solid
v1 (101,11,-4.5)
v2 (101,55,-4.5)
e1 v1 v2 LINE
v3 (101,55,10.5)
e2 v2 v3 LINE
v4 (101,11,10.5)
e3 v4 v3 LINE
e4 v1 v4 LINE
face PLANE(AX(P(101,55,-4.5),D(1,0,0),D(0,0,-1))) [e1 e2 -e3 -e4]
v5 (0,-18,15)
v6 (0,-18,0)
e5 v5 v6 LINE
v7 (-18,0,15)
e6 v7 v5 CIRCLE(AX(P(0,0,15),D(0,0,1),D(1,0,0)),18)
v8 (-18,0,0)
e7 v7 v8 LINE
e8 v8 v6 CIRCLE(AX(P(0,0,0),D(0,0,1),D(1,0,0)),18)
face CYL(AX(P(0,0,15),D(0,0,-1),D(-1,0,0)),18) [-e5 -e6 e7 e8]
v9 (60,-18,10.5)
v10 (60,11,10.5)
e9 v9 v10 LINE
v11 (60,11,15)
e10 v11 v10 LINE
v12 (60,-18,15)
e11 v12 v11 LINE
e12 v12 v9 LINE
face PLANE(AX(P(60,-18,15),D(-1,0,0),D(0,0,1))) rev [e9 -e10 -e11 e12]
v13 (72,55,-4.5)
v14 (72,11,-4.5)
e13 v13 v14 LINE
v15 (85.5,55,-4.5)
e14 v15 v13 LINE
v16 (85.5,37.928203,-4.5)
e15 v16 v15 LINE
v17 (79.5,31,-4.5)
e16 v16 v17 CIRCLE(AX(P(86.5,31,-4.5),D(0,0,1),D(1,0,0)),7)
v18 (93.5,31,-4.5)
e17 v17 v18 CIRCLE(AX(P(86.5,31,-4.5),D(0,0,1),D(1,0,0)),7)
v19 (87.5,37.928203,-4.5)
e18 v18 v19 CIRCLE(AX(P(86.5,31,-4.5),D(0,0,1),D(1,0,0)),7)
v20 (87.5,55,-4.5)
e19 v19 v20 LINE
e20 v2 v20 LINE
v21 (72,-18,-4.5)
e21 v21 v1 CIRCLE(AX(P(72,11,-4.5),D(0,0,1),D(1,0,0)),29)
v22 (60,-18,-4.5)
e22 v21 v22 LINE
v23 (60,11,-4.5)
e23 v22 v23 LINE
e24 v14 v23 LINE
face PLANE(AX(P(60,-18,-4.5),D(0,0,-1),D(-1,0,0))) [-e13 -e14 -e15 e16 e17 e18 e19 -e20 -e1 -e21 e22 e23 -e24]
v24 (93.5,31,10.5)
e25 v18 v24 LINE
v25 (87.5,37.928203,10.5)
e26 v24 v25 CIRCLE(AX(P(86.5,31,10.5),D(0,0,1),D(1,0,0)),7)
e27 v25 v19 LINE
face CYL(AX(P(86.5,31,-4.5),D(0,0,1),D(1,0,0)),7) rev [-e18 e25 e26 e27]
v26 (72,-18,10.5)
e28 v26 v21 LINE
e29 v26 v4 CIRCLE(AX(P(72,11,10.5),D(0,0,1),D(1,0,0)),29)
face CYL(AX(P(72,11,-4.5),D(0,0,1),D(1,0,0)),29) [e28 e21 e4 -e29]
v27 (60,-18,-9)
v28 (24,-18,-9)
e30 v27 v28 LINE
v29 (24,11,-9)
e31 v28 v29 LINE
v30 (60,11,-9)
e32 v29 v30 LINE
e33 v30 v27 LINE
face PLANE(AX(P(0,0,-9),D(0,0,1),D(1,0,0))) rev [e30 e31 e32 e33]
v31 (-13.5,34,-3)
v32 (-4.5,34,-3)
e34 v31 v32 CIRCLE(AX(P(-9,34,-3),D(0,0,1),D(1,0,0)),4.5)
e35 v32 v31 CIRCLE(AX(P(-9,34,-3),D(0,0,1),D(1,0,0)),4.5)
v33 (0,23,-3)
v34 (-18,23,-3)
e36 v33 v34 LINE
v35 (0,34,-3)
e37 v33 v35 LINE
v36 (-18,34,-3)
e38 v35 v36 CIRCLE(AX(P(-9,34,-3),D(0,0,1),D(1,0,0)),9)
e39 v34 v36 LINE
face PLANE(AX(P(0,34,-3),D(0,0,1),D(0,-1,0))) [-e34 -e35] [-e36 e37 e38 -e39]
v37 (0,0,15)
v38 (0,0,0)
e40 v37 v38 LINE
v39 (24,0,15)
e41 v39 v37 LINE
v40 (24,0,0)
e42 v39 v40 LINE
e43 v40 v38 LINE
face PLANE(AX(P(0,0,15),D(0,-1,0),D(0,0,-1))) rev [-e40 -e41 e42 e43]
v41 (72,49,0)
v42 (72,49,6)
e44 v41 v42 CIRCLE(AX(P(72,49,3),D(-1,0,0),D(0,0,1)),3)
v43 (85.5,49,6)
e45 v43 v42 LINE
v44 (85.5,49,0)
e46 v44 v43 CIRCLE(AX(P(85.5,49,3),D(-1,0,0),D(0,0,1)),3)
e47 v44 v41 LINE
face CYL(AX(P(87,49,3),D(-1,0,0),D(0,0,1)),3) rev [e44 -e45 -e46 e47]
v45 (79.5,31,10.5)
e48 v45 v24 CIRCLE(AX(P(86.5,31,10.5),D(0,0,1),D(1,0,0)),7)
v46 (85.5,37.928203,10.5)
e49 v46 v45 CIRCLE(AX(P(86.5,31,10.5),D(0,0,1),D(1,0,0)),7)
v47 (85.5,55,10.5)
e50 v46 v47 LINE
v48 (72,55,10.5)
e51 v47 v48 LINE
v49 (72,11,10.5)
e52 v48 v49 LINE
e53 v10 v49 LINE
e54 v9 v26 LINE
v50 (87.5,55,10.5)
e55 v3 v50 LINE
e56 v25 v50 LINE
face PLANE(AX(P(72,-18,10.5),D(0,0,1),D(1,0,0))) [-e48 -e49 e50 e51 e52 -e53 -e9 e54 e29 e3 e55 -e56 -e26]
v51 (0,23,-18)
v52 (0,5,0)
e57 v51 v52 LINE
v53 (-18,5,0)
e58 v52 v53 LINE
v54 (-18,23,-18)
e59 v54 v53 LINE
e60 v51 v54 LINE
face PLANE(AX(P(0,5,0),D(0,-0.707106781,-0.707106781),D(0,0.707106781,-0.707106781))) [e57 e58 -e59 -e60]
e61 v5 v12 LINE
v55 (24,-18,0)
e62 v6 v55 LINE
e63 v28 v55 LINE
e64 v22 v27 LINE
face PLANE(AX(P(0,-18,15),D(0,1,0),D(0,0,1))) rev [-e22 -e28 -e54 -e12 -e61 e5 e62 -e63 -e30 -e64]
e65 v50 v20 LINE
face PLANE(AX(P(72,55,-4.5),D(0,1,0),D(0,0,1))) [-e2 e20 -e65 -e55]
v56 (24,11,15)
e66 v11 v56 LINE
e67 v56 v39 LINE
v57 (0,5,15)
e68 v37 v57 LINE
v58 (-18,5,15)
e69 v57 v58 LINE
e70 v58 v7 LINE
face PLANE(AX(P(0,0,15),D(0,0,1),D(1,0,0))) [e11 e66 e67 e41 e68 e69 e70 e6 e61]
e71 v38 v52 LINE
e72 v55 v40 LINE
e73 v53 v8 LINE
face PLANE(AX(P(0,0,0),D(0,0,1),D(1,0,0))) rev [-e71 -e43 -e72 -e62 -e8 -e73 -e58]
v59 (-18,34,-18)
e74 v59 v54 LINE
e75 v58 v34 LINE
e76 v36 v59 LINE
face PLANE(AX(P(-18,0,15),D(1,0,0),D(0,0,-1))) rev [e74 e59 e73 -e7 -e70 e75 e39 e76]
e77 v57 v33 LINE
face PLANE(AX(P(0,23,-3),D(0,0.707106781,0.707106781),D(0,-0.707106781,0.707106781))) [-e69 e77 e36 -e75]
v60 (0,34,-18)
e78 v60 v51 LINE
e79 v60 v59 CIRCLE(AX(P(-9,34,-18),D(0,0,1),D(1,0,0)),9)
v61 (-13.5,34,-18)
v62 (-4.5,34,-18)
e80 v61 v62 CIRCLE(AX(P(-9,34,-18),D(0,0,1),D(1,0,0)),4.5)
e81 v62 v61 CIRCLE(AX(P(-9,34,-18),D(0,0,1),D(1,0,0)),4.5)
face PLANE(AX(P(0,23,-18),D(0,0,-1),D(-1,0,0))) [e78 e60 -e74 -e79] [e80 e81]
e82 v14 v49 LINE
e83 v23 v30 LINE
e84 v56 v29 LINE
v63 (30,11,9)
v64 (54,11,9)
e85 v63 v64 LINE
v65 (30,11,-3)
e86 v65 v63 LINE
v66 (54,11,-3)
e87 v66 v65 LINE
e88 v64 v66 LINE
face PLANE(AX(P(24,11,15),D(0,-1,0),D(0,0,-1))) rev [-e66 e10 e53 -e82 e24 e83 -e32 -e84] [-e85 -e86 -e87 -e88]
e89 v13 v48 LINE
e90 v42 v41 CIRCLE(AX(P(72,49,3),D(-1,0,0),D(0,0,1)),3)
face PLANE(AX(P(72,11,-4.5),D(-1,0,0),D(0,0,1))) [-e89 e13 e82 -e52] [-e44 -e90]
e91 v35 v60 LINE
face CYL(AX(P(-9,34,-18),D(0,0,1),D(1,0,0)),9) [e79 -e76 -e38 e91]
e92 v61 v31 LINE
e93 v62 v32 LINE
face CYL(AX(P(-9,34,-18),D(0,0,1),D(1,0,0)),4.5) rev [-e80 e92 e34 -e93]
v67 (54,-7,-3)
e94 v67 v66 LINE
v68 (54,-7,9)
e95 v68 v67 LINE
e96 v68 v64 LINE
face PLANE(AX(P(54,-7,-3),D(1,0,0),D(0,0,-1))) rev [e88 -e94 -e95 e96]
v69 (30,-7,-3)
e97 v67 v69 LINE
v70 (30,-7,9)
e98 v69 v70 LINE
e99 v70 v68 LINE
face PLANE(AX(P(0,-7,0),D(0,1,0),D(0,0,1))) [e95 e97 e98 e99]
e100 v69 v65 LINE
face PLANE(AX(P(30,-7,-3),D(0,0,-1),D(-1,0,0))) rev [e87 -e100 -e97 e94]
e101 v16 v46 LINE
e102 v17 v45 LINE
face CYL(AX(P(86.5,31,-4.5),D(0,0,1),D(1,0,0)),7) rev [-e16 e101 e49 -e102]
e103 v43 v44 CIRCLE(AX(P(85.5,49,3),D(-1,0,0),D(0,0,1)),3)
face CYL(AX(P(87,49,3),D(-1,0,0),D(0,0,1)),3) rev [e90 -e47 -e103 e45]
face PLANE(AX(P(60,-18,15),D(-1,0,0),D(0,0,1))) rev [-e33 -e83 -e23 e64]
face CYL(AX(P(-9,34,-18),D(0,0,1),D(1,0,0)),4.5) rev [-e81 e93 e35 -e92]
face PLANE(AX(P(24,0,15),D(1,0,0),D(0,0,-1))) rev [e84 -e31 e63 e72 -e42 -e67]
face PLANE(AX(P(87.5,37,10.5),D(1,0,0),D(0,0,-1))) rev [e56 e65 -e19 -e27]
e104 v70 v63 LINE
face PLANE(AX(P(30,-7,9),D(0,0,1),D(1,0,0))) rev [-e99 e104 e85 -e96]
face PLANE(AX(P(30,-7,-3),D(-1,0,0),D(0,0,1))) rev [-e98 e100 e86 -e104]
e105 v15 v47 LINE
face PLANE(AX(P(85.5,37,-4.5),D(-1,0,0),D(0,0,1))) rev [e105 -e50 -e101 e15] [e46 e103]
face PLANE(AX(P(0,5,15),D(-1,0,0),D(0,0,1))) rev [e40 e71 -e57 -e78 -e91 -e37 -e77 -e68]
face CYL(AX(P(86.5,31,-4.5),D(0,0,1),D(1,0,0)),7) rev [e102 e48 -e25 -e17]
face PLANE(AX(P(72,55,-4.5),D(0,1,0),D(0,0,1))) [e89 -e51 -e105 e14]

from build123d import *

# Parameters (mm, degrees)
BASE_BODY_DEPTH             = 15
ARM_BLOCK_DEPTH             = 18
INCLINED_ARM_SKETCH_W       = 15
INCLINED_ARM_SKETCH_H       = 11
INCLINED_ARM_DEPTH          = 18
TOP_LUG_DEPTH               = 15
LUG_HOLE_SKETCH_R           = 4.5
LUG_HOLE_9_DEPTH            = 15
POCKET_BOSS_SKETCH_W        = 36
POCKET_BOSS_SKETCH_H        = 29
POCKET_BOSS_DEPTH           = 9
CLEVIS_BLOCK_SKETCH_W       = 12
CLEVIS_BLOCK_SKETCH_H       = 15
CLEVIS_BLOCK_DEPTH          = 29
CLEVIS_CORNER_DEPTH         = 15
CLEVIS_JAW_DEPTH            = 15
CLEVIS_HOLE_SKETCH_R        = 7
CLEVIS_HOLE_14_DEPTH        = 15
CLEVIS_SLOT_DEPTH           = 18
JAW_HOLE_SKETCH_R           = 3
JAW_HOLE_6_DEPTH            = 15
RECTANGULAR_POCKET_SKETCH_W = 24
RECTANGULAR_POCKET_SKETCH_H = 12
RECTANGULAR_POCKET_DEPTH    = 18


with BuildPart() as part:
    # Base Profile Sketch → Base Body (new body)
    with BuildSketch(Plane.XY):
        with BuildLine():
            Line((0, -18), (60, -18))
            Line((60, -18), (60, 11))
            Line((60, 11), (24, 11))
            Line((24, 11), (24, 0))
            Line((24, 0), (0, 0))
            Line((0, 0), (0, 5))
            Line((0, 5), (-18, 5))
            Line((-18, 5), (-18, 0))
            ThreePointArc((-18, 0), (-12.727922061, -12.727922061), (0, -18))
        make_face()
    extrude(amount=BASE_BODY_DEPTH)

    # Arm Block Sketch → Arm Block (add)
    with BuildSketch(Plane.ZY.offset(18)):
        Polygon((-18, 23), (-3, 23), (15, 5), (0, 5), align=None)
    extrude(amount=-ARM_BLOCK_DEPTH)

    # Inclined Arm Sketch → Inclined Arm (add)
    with BuildSketch(Plane.ZY.offset(18)):
        with Locations((-10.5, 28.5)):
            Rectangle(INCLINED_ARM_SKETCH_W, INCLINED_ARM_SKETCH_H)
    extrude(amount=-INCLINED_ARM_DEPTH)

    # Top Lug Sketch → Top Lug (add)
    with BuildSketch(Plane.XY.offset(-3)):
        with BuildLine():
            Line((-18, 34), (0, 34))
            ThreePointArc((0, 34), (-9, 43), (-18, 34))
        make_face()
    extrude(amount=-TOP_LUG_DEPTH)

    # Lug Hole Sketch → Lug Hole Ø9 (cut)
    with BuildSketch(Plane.XY.offset(-3)):
        with Locations((-9, 34)):
            Circle(LUG_HOLE_SKETCH_R)
    extrude(amount=-LUG_HOLE_9_DEPTH, mode=Mode.SUBTRACT)

    # Pocket Boss Sketch → Pocket Boss (add)
    with BuildSketch(Plane(origin=(0, 0, 0), x_dir=(-1, 0, 0), z_dir=(0, 0, -1))):
        with Locations((-42, -3.5)):
            Rectangle(POCKET_BOSS_SKETCH_W, POCKET_BOSS_SKETCH_H)
    extrude(amount=POCKET_BOSS_DEPTH)

    # Clevis Block Sketch → Clevis Block (add)
    with BuildSketch(Plane(origin=(0, 11, 0), x_dir=(1, 0, 0), z_dir=(0, 1, 0))):
        with Locations((66, -3)):
            Rectangle(CLEVIS_BLOCK_SKETCH_W, CLEVIS_BLOCK_SKETCH_H)
    extrude(amount=-CLEVIS_BLOCK_DEPTH)

    # Clevis Corner Sketch → Clevis Corner (add)
    with BuildSketch(Plane.XY.offset(10.5)):
        with BuildLine():
            Line((72, 11), (101, 11))
            ThreePointArc((101, 11), (92.506096654, -9.506096654), (72, -18))
            Line((72, -18), (72, 11))
        make_face()
    extrude(amount=-CLEVIS_CORNER_DEPTH)

    # Clevis Jaw Sketch → Clevis Jaw (add)
    with BuildSketch(Plane.XY.offset(10.5)):
        Polygon((101, 11), (72, 11), (72, 31), (72, 55), (101, 55), align=None)
    extrude(amount=-CLEVIS_JAW_DEPTH)

    # Clevis Hole Sketch → Clevis Hole Ø14 (cut)
    with BuildSketch(Plane.XY.offset(10.5)):
        with Locations((86.5, 31)):
            Circle(CLEVIS_HOLE_SKETCH_R)
    extrude(amount=-CLEVIS_HOLE_14_DEPTH, mode=Mode.SUBTRACT)

    # Clevis Slot Sketch → Clevis Slot (cut)
    with BuildSketch(Plane(origin=(0, 55, 0), x_dir=(1, 0, 0), z_dir=(0, 1, 0))):
        Polygon((86.5, 4.5), (85.5, 4.5), (85.5, -10.5), (87.5, -10.5), (87.5, 4.5), align=None)
    extrude(amount=-CLEVIS_SLOT_DEPTH, mode=Mode.SUBTRACT)

    # Jaw Hole Sketch → Jaw Hole Ø6 (cut)
    with BuildSketch(Plane.ZY.offset(-72)):
        with Locations((3, 49)):
            Circle(JAW_HOLE_SKETCH_R)
    extrude(amount=-JAW_HOLE_6_DEPTH, mode=Mode.SUBTRACT)

    # Rectangular Pocket Sketch → Rectangular Pocket (cut)
    with BuildSketch(Plane(origin=(0, 11, 0), x_dir=(1, 0, 0), z_dir=(0, 1, 0))):
        with Locations((42, -3)):
            Rectangle(RECTANGULAR_POCKET_SKETCH_W, RECTANGULAR_POCKET_SKETCH_H)
    extrude(amount=-RECTANGULAR_POCKET_DEPTH, mode=Mode.SUBTRACT)


solid = part.part
